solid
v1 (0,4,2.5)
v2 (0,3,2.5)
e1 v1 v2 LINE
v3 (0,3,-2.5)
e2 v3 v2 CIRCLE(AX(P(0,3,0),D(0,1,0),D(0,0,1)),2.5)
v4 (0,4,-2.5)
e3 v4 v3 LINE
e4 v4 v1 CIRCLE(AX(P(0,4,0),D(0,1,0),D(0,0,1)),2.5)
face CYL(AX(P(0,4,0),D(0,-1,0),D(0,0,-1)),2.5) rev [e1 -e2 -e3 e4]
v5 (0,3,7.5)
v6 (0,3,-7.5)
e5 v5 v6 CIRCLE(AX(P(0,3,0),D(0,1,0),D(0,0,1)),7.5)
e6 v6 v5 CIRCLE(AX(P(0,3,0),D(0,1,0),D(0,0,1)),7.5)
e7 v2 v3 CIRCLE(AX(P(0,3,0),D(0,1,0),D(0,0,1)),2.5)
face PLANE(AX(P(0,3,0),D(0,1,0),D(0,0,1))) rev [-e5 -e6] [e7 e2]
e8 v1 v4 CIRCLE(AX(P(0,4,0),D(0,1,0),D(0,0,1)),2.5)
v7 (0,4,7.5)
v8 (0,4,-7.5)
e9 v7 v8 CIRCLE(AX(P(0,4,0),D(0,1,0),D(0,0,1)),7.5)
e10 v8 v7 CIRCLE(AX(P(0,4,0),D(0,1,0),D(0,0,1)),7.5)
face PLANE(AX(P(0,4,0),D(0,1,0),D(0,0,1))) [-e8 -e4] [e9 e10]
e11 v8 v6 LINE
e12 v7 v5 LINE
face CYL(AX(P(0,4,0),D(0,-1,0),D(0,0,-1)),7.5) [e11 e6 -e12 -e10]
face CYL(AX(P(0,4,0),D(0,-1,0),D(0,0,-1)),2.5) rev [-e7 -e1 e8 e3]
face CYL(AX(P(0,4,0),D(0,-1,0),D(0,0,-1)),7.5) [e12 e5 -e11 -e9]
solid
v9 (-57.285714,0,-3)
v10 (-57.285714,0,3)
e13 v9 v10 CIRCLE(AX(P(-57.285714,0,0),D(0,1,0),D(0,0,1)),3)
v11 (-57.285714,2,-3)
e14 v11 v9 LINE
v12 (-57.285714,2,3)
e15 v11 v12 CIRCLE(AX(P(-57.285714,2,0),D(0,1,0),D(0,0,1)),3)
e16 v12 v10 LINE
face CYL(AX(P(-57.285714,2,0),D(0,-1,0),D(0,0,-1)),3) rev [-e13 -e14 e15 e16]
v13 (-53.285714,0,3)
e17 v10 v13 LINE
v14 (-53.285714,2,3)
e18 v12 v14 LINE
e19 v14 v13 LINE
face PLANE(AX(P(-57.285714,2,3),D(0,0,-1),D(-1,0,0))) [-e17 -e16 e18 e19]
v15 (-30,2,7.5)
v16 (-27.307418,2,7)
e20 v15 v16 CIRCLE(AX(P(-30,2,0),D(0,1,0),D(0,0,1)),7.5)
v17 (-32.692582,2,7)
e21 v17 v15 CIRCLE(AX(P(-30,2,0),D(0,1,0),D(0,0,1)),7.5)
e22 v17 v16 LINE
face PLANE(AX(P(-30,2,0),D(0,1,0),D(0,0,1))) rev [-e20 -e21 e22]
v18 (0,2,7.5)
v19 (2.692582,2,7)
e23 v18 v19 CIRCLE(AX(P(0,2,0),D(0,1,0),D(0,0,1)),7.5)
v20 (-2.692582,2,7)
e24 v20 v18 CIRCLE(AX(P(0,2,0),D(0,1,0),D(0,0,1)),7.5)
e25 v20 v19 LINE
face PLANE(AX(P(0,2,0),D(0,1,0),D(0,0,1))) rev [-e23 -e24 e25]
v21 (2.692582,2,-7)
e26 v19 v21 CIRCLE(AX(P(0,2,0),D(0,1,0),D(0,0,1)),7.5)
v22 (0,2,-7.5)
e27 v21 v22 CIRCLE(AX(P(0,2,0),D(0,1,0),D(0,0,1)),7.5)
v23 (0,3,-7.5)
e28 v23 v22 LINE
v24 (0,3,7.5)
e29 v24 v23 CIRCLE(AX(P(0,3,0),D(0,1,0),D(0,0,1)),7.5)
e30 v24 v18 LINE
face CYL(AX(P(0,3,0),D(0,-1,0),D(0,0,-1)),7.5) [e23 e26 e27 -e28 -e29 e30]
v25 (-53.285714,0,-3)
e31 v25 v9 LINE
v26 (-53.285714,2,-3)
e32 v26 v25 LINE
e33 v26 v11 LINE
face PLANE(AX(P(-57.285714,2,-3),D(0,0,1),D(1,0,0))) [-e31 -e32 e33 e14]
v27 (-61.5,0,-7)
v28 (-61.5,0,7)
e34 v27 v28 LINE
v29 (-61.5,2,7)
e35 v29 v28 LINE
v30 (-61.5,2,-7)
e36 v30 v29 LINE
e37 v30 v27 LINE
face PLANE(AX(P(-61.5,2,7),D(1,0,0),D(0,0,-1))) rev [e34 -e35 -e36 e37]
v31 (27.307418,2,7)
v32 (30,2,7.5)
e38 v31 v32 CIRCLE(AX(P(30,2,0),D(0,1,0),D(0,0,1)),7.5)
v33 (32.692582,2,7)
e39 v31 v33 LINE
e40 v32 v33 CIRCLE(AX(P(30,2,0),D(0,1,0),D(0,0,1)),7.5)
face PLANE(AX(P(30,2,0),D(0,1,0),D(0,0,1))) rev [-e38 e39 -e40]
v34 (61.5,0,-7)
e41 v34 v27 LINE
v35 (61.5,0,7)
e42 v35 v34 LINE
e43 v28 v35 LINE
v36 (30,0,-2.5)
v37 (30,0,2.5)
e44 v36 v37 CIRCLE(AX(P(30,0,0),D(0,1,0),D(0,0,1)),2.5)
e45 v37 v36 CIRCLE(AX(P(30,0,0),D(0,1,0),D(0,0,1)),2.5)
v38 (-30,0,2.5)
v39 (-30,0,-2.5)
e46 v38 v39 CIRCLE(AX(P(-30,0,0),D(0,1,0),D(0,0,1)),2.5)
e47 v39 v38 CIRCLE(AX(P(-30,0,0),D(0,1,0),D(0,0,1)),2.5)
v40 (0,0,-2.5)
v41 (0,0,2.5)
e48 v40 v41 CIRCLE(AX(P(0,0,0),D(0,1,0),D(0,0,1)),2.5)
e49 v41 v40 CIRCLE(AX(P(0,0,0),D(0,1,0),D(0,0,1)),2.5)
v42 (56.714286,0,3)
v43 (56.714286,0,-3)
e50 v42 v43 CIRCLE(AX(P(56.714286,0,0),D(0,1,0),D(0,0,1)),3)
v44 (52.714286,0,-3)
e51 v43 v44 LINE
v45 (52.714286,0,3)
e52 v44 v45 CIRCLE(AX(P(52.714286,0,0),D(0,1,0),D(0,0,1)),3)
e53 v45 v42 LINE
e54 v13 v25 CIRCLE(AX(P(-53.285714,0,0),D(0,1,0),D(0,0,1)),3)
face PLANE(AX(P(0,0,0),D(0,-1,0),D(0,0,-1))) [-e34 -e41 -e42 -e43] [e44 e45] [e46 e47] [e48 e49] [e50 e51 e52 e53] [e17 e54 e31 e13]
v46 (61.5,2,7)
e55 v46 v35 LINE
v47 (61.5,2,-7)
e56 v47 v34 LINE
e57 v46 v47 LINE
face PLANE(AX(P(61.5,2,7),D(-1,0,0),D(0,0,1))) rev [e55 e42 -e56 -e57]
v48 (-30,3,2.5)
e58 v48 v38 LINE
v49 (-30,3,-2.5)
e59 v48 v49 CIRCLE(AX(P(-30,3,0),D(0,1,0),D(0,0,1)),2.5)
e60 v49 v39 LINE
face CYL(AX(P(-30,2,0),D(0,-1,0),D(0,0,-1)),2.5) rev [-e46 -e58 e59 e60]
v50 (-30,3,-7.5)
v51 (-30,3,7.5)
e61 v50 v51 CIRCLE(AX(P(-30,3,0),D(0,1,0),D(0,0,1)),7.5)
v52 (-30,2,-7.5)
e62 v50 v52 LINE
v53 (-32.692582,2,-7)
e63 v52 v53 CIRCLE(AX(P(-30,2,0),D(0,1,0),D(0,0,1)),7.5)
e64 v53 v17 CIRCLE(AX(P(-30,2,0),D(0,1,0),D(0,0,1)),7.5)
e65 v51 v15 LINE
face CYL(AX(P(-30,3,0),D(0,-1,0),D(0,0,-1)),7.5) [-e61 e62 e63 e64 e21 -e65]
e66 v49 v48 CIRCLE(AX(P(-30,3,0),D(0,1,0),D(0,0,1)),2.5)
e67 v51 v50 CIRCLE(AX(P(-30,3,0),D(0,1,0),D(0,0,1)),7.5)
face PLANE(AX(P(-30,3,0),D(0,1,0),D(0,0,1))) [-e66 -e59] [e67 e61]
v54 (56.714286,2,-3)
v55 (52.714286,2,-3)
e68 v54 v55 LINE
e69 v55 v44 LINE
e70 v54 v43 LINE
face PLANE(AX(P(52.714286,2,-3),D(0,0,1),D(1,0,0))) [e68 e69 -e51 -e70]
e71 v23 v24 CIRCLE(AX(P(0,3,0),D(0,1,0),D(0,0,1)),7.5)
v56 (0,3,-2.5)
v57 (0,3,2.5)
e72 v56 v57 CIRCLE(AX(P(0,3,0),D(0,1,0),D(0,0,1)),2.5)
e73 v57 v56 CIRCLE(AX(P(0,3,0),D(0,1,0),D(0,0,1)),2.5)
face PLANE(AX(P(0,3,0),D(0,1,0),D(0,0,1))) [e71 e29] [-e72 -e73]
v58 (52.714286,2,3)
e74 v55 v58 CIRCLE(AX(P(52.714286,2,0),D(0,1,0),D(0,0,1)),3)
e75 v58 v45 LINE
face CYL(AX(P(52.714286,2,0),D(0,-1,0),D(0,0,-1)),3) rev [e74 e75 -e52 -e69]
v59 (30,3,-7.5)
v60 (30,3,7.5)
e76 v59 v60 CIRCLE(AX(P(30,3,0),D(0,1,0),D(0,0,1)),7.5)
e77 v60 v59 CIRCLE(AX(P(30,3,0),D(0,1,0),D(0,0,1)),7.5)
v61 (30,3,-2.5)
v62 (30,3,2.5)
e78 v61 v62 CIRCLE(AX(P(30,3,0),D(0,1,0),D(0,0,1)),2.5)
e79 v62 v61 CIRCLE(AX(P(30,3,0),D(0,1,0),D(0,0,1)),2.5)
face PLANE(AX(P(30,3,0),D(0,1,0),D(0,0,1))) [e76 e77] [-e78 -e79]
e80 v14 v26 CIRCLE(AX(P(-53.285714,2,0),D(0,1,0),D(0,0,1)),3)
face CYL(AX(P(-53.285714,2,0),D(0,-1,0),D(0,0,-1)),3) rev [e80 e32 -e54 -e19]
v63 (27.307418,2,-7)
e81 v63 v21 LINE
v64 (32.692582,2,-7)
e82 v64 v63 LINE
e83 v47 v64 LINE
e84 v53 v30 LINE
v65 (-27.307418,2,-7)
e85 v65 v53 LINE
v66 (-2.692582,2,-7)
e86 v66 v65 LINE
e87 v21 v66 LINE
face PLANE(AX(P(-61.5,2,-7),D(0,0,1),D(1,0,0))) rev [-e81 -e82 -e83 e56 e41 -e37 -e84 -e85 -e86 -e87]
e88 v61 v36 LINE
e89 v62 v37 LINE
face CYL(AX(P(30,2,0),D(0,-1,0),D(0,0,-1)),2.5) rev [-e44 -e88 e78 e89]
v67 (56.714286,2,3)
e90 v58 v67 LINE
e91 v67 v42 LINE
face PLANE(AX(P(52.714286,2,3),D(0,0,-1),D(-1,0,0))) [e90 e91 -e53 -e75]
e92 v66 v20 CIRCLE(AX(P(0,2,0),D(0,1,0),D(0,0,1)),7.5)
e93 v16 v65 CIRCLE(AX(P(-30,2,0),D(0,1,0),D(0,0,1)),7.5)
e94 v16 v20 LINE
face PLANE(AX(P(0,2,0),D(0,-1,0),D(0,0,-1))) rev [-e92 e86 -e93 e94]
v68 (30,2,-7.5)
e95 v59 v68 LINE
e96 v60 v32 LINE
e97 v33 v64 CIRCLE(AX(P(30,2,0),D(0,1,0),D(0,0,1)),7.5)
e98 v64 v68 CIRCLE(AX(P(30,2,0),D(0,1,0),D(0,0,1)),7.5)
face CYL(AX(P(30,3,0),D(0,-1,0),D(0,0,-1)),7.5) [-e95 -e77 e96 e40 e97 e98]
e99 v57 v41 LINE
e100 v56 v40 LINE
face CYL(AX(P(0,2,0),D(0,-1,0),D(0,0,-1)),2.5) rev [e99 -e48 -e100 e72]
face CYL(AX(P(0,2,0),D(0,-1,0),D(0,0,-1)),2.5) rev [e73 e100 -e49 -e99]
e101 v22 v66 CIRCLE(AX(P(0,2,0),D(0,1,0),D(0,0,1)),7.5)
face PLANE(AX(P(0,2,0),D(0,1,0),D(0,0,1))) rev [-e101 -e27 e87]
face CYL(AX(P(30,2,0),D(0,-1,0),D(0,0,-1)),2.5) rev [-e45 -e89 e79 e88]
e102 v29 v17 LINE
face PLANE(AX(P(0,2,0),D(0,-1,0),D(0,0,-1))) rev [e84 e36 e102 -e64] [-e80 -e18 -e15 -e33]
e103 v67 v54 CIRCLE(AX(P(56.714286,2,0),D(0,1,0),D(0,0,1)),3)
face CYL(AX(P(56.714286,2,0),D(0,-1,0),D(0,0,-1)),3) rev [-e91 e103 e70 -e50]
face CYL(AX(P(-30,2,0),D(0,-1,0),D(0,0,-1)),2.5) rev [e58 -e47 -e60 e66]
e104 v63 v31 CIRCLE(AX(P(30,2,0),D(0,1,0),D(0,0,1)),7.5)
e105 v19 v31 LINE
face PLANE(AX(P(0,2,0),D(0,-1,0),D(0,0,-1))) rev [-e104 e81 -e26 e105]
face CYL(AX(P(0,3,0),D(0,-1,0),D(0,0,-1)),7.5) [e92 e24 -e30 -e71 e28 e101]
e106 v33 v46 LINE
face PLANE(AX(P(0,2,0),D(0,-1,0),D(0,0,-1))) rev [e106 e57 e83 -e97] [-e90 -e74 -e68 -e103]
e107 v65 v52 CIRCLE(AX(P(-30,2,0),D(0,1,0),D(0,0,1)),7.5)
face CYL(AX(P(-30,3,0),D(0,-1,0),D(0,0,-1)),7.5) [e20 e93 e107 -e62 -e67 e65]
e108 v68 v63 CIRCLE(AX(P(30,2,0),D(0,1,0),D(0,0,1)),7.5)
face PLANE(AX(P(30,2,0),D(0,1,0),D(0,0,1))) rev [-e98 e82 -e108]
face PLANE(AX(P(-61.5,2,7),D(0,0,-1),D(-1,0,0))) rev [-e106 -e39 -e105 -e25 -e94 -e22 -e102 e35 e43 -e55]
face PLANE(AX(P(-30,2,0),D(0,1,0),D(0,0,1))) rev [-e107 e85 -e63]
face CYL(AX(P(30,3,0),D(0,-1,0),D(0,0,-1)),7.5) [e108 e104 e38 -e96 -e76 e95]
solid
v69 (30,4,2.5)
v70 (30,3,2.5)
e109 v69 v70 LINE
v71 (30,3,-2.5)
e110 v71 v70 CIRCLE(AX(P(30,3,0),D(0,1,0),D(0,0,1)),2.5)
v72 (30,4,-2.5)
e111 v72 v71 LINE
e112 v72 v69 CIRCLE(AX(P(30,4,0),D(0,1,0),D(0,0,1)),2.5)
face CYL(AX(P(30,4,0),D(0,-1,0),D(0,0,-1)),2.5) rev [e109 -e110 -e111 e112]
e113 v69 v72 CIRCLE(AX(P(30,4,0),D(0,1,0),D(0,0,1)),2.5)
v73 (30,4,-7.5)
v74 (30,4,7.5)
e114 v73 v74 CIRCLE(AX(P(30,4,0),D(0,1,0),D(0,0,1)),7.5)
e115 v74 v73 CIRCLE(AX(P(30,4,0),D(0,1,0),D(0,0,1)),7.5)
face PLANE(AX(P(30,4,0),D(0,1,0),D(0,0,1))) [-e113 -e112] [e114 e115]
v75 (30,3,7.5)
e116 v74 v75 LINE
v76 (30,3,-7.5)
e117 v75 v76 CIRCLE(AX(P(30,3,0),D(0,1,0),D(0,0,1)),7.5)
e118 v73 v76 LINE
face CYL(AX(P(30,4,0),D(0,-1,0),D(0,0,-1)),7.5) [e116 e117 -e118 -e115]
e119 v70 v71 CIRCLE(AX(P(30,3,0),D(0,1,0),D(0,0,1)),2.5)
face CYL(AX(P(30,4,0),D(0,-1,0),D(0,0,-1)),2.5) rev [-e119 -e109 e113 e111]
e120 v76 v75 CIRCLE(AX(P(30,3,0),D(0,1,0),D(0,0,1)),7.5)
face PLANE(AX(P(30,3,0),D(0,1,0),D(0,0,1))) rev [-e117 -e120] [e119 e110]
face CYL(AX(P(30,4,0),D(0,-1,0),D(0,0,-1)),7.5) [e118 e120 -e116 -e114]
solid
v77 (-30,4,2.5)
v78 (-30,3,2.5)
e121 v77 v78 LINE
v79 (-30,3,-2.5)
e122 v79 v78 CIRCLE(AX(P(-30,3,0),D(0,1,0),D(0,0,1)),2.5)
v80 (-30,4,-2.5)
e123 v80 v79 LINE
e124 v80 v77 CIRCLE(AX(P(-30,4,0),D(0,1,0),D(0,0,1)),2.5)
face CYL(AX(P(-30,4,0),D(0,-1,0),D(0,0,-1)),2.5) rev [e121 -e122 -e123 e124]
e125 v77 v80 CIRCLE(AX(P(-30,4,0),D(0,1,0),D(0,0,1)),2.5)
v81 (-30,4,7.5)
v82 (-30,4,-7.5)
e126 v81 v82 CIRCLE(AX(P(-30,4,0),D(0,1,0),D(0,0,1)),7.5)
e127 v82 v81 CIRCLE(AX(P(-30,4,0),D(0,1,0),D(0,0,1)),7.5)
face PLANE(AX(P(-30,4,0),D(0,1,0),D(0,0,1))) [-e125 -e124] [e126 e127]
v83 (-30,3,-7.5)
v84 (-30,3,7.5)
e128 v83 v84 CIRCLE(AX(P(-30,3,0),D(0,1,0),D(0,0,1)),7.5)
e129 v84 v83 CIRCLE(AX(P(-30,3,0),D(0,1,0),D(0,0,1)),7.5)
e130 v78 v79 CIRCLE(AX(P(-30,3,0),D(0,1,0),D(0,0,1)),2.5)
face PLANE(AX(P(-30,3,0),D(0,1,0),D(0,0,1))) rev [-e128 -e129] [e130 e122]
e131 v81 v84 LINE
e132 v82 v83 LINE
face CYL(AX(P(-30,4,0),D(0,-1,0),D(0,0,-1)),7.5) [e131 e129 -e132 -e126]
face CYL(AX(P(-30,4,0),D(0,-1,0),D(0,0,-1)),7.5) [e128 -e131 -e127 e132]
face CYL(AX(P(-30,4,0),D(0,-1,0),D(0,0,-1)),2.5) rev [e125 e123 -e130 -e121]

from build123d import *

# Parameters (mm, degrees)
SKETCH1_W             = 123
SKETCH1_H             = 14
SKETCH1_R             = 2.5
BOSS_EXTRUDE1_DEPTH   = 2
SKETCH2_R             = 7.5
SKETCH2_R_2           = 2.5
BOSS_EXTRUDE2_DEPTH   = 1
SKETCH3_R             = 7.5
SKETCH3_R_2           = 2.5
BOSS_EXTRUDE3_DEPTH   = 1
BOSS_EXTRUDE3_2_DEPTH = 1
BOSS_EXTRUDE3_3_DEPTH = 1


with BuildPart() as part:
    # Sketch1 → Boss-Extrude1 (new body)
    with BuildSketch(Plane(origin=(0, 0, 0), x_dir=(1, 0, 0), z_dir=(0, 1, 0))):
        Rectangle(SKETCH1_W, SKETCH1_H)
        with Locations(Location((-30, 0, 0), (0, 0, 270))):
            Circle(SKETCH1_R, mode=Mode.SUBTRACT)
        with Locations(Location((0, 0, 0), (0, 0, 270))):
            Circle(SKETCH1_R, mode=Mode.SUBTRACT)
        with Locations(Location((30, 0, 0), (0, 0, 270))):
            Circle(SKETCH1_R, mode=Mode.SUBTRACT)
        with BuildLine():
            Line((-57.285714286, 3), (-53.285714286, 3))
            ThreePointArc((-53.285714286, 3), (-50.285714286, 0), (-53.285714286, -3))
            Line((-53.285714286, -3), (-57.285714286, -3))
            ThreePointArc((-57.285714286, -3), (-60.285714286, 0), (-57.285714286, 3))
        make_face(mode=Mode.SUBTRACT)
        with BuildLine():
            Line((52.714285714, 3), (56.714285714, 3))
            ThreePointArc((56.714285714, 3), (59.714285714, 0), (56.714285714, -3))
            Line((56.714285714, -3), (52.714285714, -3))
            ThreePointArc((52.714285714, -3), (49.714285714, 0), (52.714285714, 3))
        make_face(mode=Mode.SUBTRACT)
    extrude(amount=BOSS_EXTRUDE1_DEPTH)

    # Sketch2 → Boss-Extrude2 (add)
    # profile 1 of 3: a face of its own
    with BuildSketch(Plane(origin=(0, 2, 0), x_dir=(1, 0, 0), z_dir=(0, 1, 0))):
        with Locations(Location((-30, 0, 0), (0, 0, 68.960530219))):
            Circle(SKETCH2_R)
        with Locations(Location((-30, 0, 0), (0, 0, 270))):
            Circle(SKETCH2_R_2, mode=Mode.SUBTRACT)
    # profile 2 of 3: a face of its own
    with BuildSketch(Plane(origin=(0, 2, 0), x_dir=(1, 0, 0), z_dir=(0, 1, 0))):
        with Locations(Location((0, 0, 0), (0, 0, 111.039469781))):
            Circle(SKETCH2_R)
        with Locations(Location((0, 0, 0), (0, 0, 270))):
            Circle(SKETCH2_R_2, mode=Mode.SUBTRACT)
    # profile 3 of 3: a face of its own
    with BuildSketch(Plane(origin=(0, 2, 0), x_dir=(1, 0, 0), z_dir=(0, 1, 0))):
        with Locations(Location((30, 0, 0), (0, 0, 68.960530219))):
            Circle(SKETCH2_R)
        with Locations(Location((30, 0, 0), (0, 0, 270))):
            Circle(SKETCH2_R_2, mode=Mode.SUBTRACT)
    extrude(amount=BOSS_EXTRUDE2_DEPTH)


with BuildPart() as body_2:
    # Sketch3 → Boss-Extrude3 (new body)
    with BuildSketch(Plane(origin=(0, 3, 0), x_dir=(1, 0, 0), z_dir=(0, 1, 0))):
        with Locations(Location((-30, 0, 0), (0, 0, 270))):
            Circle(SKETCH3_R)
        with Locations(Location((-30, 0, 0), (0, 0, 270))):
            Circle(SKETCH3_R_2, mode=Mode.SUBTRACT)
    extrude(amount=BOSS_EXTRUDE3_DEPTH)


with BuildPart() as body_3:
    # Sketch3 → Boss-Extrude3 2 (new body)
    with BuildSketch(Plane(origin=(0, 3, 0), x_dir=(1, 0, 0), z_dir=(0, 1, 0))):
        with Locations(Location((0, 0, 0), (0, 0, 270))):
            Circle(SKETCH3_R)
        with Locations(Location((0, 0, 0), (0, 0, 270))):
            Circle(SKETCH3_R_2, mode=Mode.SUBTRACT)
    extrude(amount=BOSS_EXTRUDE3_2_DEPTH)


with BuildPart() as body_4:
    # Sketch3 → Boss-Extrude3 3 (new body)
    with BuildSketch(Plane(origin=(0, 3, 0), x_dir=(1, 0, 0), z_dir=(0, 1, 0))):
        with Locations(Location((30, 0, 0), (0, 0, 270))):
            Circle(SKETCH3_R)
        with Locations(Location((30, 0, 0), (0, 0, 270))):
            Circle(SKETCH3_R_2, mode=Mode.SUBTRACT)
    extrude(amount=BOSS_EXTRUDE3_3_DEPTH)


solid = Compound([part.part, body_2.part, body_3.part, body_4.part])
